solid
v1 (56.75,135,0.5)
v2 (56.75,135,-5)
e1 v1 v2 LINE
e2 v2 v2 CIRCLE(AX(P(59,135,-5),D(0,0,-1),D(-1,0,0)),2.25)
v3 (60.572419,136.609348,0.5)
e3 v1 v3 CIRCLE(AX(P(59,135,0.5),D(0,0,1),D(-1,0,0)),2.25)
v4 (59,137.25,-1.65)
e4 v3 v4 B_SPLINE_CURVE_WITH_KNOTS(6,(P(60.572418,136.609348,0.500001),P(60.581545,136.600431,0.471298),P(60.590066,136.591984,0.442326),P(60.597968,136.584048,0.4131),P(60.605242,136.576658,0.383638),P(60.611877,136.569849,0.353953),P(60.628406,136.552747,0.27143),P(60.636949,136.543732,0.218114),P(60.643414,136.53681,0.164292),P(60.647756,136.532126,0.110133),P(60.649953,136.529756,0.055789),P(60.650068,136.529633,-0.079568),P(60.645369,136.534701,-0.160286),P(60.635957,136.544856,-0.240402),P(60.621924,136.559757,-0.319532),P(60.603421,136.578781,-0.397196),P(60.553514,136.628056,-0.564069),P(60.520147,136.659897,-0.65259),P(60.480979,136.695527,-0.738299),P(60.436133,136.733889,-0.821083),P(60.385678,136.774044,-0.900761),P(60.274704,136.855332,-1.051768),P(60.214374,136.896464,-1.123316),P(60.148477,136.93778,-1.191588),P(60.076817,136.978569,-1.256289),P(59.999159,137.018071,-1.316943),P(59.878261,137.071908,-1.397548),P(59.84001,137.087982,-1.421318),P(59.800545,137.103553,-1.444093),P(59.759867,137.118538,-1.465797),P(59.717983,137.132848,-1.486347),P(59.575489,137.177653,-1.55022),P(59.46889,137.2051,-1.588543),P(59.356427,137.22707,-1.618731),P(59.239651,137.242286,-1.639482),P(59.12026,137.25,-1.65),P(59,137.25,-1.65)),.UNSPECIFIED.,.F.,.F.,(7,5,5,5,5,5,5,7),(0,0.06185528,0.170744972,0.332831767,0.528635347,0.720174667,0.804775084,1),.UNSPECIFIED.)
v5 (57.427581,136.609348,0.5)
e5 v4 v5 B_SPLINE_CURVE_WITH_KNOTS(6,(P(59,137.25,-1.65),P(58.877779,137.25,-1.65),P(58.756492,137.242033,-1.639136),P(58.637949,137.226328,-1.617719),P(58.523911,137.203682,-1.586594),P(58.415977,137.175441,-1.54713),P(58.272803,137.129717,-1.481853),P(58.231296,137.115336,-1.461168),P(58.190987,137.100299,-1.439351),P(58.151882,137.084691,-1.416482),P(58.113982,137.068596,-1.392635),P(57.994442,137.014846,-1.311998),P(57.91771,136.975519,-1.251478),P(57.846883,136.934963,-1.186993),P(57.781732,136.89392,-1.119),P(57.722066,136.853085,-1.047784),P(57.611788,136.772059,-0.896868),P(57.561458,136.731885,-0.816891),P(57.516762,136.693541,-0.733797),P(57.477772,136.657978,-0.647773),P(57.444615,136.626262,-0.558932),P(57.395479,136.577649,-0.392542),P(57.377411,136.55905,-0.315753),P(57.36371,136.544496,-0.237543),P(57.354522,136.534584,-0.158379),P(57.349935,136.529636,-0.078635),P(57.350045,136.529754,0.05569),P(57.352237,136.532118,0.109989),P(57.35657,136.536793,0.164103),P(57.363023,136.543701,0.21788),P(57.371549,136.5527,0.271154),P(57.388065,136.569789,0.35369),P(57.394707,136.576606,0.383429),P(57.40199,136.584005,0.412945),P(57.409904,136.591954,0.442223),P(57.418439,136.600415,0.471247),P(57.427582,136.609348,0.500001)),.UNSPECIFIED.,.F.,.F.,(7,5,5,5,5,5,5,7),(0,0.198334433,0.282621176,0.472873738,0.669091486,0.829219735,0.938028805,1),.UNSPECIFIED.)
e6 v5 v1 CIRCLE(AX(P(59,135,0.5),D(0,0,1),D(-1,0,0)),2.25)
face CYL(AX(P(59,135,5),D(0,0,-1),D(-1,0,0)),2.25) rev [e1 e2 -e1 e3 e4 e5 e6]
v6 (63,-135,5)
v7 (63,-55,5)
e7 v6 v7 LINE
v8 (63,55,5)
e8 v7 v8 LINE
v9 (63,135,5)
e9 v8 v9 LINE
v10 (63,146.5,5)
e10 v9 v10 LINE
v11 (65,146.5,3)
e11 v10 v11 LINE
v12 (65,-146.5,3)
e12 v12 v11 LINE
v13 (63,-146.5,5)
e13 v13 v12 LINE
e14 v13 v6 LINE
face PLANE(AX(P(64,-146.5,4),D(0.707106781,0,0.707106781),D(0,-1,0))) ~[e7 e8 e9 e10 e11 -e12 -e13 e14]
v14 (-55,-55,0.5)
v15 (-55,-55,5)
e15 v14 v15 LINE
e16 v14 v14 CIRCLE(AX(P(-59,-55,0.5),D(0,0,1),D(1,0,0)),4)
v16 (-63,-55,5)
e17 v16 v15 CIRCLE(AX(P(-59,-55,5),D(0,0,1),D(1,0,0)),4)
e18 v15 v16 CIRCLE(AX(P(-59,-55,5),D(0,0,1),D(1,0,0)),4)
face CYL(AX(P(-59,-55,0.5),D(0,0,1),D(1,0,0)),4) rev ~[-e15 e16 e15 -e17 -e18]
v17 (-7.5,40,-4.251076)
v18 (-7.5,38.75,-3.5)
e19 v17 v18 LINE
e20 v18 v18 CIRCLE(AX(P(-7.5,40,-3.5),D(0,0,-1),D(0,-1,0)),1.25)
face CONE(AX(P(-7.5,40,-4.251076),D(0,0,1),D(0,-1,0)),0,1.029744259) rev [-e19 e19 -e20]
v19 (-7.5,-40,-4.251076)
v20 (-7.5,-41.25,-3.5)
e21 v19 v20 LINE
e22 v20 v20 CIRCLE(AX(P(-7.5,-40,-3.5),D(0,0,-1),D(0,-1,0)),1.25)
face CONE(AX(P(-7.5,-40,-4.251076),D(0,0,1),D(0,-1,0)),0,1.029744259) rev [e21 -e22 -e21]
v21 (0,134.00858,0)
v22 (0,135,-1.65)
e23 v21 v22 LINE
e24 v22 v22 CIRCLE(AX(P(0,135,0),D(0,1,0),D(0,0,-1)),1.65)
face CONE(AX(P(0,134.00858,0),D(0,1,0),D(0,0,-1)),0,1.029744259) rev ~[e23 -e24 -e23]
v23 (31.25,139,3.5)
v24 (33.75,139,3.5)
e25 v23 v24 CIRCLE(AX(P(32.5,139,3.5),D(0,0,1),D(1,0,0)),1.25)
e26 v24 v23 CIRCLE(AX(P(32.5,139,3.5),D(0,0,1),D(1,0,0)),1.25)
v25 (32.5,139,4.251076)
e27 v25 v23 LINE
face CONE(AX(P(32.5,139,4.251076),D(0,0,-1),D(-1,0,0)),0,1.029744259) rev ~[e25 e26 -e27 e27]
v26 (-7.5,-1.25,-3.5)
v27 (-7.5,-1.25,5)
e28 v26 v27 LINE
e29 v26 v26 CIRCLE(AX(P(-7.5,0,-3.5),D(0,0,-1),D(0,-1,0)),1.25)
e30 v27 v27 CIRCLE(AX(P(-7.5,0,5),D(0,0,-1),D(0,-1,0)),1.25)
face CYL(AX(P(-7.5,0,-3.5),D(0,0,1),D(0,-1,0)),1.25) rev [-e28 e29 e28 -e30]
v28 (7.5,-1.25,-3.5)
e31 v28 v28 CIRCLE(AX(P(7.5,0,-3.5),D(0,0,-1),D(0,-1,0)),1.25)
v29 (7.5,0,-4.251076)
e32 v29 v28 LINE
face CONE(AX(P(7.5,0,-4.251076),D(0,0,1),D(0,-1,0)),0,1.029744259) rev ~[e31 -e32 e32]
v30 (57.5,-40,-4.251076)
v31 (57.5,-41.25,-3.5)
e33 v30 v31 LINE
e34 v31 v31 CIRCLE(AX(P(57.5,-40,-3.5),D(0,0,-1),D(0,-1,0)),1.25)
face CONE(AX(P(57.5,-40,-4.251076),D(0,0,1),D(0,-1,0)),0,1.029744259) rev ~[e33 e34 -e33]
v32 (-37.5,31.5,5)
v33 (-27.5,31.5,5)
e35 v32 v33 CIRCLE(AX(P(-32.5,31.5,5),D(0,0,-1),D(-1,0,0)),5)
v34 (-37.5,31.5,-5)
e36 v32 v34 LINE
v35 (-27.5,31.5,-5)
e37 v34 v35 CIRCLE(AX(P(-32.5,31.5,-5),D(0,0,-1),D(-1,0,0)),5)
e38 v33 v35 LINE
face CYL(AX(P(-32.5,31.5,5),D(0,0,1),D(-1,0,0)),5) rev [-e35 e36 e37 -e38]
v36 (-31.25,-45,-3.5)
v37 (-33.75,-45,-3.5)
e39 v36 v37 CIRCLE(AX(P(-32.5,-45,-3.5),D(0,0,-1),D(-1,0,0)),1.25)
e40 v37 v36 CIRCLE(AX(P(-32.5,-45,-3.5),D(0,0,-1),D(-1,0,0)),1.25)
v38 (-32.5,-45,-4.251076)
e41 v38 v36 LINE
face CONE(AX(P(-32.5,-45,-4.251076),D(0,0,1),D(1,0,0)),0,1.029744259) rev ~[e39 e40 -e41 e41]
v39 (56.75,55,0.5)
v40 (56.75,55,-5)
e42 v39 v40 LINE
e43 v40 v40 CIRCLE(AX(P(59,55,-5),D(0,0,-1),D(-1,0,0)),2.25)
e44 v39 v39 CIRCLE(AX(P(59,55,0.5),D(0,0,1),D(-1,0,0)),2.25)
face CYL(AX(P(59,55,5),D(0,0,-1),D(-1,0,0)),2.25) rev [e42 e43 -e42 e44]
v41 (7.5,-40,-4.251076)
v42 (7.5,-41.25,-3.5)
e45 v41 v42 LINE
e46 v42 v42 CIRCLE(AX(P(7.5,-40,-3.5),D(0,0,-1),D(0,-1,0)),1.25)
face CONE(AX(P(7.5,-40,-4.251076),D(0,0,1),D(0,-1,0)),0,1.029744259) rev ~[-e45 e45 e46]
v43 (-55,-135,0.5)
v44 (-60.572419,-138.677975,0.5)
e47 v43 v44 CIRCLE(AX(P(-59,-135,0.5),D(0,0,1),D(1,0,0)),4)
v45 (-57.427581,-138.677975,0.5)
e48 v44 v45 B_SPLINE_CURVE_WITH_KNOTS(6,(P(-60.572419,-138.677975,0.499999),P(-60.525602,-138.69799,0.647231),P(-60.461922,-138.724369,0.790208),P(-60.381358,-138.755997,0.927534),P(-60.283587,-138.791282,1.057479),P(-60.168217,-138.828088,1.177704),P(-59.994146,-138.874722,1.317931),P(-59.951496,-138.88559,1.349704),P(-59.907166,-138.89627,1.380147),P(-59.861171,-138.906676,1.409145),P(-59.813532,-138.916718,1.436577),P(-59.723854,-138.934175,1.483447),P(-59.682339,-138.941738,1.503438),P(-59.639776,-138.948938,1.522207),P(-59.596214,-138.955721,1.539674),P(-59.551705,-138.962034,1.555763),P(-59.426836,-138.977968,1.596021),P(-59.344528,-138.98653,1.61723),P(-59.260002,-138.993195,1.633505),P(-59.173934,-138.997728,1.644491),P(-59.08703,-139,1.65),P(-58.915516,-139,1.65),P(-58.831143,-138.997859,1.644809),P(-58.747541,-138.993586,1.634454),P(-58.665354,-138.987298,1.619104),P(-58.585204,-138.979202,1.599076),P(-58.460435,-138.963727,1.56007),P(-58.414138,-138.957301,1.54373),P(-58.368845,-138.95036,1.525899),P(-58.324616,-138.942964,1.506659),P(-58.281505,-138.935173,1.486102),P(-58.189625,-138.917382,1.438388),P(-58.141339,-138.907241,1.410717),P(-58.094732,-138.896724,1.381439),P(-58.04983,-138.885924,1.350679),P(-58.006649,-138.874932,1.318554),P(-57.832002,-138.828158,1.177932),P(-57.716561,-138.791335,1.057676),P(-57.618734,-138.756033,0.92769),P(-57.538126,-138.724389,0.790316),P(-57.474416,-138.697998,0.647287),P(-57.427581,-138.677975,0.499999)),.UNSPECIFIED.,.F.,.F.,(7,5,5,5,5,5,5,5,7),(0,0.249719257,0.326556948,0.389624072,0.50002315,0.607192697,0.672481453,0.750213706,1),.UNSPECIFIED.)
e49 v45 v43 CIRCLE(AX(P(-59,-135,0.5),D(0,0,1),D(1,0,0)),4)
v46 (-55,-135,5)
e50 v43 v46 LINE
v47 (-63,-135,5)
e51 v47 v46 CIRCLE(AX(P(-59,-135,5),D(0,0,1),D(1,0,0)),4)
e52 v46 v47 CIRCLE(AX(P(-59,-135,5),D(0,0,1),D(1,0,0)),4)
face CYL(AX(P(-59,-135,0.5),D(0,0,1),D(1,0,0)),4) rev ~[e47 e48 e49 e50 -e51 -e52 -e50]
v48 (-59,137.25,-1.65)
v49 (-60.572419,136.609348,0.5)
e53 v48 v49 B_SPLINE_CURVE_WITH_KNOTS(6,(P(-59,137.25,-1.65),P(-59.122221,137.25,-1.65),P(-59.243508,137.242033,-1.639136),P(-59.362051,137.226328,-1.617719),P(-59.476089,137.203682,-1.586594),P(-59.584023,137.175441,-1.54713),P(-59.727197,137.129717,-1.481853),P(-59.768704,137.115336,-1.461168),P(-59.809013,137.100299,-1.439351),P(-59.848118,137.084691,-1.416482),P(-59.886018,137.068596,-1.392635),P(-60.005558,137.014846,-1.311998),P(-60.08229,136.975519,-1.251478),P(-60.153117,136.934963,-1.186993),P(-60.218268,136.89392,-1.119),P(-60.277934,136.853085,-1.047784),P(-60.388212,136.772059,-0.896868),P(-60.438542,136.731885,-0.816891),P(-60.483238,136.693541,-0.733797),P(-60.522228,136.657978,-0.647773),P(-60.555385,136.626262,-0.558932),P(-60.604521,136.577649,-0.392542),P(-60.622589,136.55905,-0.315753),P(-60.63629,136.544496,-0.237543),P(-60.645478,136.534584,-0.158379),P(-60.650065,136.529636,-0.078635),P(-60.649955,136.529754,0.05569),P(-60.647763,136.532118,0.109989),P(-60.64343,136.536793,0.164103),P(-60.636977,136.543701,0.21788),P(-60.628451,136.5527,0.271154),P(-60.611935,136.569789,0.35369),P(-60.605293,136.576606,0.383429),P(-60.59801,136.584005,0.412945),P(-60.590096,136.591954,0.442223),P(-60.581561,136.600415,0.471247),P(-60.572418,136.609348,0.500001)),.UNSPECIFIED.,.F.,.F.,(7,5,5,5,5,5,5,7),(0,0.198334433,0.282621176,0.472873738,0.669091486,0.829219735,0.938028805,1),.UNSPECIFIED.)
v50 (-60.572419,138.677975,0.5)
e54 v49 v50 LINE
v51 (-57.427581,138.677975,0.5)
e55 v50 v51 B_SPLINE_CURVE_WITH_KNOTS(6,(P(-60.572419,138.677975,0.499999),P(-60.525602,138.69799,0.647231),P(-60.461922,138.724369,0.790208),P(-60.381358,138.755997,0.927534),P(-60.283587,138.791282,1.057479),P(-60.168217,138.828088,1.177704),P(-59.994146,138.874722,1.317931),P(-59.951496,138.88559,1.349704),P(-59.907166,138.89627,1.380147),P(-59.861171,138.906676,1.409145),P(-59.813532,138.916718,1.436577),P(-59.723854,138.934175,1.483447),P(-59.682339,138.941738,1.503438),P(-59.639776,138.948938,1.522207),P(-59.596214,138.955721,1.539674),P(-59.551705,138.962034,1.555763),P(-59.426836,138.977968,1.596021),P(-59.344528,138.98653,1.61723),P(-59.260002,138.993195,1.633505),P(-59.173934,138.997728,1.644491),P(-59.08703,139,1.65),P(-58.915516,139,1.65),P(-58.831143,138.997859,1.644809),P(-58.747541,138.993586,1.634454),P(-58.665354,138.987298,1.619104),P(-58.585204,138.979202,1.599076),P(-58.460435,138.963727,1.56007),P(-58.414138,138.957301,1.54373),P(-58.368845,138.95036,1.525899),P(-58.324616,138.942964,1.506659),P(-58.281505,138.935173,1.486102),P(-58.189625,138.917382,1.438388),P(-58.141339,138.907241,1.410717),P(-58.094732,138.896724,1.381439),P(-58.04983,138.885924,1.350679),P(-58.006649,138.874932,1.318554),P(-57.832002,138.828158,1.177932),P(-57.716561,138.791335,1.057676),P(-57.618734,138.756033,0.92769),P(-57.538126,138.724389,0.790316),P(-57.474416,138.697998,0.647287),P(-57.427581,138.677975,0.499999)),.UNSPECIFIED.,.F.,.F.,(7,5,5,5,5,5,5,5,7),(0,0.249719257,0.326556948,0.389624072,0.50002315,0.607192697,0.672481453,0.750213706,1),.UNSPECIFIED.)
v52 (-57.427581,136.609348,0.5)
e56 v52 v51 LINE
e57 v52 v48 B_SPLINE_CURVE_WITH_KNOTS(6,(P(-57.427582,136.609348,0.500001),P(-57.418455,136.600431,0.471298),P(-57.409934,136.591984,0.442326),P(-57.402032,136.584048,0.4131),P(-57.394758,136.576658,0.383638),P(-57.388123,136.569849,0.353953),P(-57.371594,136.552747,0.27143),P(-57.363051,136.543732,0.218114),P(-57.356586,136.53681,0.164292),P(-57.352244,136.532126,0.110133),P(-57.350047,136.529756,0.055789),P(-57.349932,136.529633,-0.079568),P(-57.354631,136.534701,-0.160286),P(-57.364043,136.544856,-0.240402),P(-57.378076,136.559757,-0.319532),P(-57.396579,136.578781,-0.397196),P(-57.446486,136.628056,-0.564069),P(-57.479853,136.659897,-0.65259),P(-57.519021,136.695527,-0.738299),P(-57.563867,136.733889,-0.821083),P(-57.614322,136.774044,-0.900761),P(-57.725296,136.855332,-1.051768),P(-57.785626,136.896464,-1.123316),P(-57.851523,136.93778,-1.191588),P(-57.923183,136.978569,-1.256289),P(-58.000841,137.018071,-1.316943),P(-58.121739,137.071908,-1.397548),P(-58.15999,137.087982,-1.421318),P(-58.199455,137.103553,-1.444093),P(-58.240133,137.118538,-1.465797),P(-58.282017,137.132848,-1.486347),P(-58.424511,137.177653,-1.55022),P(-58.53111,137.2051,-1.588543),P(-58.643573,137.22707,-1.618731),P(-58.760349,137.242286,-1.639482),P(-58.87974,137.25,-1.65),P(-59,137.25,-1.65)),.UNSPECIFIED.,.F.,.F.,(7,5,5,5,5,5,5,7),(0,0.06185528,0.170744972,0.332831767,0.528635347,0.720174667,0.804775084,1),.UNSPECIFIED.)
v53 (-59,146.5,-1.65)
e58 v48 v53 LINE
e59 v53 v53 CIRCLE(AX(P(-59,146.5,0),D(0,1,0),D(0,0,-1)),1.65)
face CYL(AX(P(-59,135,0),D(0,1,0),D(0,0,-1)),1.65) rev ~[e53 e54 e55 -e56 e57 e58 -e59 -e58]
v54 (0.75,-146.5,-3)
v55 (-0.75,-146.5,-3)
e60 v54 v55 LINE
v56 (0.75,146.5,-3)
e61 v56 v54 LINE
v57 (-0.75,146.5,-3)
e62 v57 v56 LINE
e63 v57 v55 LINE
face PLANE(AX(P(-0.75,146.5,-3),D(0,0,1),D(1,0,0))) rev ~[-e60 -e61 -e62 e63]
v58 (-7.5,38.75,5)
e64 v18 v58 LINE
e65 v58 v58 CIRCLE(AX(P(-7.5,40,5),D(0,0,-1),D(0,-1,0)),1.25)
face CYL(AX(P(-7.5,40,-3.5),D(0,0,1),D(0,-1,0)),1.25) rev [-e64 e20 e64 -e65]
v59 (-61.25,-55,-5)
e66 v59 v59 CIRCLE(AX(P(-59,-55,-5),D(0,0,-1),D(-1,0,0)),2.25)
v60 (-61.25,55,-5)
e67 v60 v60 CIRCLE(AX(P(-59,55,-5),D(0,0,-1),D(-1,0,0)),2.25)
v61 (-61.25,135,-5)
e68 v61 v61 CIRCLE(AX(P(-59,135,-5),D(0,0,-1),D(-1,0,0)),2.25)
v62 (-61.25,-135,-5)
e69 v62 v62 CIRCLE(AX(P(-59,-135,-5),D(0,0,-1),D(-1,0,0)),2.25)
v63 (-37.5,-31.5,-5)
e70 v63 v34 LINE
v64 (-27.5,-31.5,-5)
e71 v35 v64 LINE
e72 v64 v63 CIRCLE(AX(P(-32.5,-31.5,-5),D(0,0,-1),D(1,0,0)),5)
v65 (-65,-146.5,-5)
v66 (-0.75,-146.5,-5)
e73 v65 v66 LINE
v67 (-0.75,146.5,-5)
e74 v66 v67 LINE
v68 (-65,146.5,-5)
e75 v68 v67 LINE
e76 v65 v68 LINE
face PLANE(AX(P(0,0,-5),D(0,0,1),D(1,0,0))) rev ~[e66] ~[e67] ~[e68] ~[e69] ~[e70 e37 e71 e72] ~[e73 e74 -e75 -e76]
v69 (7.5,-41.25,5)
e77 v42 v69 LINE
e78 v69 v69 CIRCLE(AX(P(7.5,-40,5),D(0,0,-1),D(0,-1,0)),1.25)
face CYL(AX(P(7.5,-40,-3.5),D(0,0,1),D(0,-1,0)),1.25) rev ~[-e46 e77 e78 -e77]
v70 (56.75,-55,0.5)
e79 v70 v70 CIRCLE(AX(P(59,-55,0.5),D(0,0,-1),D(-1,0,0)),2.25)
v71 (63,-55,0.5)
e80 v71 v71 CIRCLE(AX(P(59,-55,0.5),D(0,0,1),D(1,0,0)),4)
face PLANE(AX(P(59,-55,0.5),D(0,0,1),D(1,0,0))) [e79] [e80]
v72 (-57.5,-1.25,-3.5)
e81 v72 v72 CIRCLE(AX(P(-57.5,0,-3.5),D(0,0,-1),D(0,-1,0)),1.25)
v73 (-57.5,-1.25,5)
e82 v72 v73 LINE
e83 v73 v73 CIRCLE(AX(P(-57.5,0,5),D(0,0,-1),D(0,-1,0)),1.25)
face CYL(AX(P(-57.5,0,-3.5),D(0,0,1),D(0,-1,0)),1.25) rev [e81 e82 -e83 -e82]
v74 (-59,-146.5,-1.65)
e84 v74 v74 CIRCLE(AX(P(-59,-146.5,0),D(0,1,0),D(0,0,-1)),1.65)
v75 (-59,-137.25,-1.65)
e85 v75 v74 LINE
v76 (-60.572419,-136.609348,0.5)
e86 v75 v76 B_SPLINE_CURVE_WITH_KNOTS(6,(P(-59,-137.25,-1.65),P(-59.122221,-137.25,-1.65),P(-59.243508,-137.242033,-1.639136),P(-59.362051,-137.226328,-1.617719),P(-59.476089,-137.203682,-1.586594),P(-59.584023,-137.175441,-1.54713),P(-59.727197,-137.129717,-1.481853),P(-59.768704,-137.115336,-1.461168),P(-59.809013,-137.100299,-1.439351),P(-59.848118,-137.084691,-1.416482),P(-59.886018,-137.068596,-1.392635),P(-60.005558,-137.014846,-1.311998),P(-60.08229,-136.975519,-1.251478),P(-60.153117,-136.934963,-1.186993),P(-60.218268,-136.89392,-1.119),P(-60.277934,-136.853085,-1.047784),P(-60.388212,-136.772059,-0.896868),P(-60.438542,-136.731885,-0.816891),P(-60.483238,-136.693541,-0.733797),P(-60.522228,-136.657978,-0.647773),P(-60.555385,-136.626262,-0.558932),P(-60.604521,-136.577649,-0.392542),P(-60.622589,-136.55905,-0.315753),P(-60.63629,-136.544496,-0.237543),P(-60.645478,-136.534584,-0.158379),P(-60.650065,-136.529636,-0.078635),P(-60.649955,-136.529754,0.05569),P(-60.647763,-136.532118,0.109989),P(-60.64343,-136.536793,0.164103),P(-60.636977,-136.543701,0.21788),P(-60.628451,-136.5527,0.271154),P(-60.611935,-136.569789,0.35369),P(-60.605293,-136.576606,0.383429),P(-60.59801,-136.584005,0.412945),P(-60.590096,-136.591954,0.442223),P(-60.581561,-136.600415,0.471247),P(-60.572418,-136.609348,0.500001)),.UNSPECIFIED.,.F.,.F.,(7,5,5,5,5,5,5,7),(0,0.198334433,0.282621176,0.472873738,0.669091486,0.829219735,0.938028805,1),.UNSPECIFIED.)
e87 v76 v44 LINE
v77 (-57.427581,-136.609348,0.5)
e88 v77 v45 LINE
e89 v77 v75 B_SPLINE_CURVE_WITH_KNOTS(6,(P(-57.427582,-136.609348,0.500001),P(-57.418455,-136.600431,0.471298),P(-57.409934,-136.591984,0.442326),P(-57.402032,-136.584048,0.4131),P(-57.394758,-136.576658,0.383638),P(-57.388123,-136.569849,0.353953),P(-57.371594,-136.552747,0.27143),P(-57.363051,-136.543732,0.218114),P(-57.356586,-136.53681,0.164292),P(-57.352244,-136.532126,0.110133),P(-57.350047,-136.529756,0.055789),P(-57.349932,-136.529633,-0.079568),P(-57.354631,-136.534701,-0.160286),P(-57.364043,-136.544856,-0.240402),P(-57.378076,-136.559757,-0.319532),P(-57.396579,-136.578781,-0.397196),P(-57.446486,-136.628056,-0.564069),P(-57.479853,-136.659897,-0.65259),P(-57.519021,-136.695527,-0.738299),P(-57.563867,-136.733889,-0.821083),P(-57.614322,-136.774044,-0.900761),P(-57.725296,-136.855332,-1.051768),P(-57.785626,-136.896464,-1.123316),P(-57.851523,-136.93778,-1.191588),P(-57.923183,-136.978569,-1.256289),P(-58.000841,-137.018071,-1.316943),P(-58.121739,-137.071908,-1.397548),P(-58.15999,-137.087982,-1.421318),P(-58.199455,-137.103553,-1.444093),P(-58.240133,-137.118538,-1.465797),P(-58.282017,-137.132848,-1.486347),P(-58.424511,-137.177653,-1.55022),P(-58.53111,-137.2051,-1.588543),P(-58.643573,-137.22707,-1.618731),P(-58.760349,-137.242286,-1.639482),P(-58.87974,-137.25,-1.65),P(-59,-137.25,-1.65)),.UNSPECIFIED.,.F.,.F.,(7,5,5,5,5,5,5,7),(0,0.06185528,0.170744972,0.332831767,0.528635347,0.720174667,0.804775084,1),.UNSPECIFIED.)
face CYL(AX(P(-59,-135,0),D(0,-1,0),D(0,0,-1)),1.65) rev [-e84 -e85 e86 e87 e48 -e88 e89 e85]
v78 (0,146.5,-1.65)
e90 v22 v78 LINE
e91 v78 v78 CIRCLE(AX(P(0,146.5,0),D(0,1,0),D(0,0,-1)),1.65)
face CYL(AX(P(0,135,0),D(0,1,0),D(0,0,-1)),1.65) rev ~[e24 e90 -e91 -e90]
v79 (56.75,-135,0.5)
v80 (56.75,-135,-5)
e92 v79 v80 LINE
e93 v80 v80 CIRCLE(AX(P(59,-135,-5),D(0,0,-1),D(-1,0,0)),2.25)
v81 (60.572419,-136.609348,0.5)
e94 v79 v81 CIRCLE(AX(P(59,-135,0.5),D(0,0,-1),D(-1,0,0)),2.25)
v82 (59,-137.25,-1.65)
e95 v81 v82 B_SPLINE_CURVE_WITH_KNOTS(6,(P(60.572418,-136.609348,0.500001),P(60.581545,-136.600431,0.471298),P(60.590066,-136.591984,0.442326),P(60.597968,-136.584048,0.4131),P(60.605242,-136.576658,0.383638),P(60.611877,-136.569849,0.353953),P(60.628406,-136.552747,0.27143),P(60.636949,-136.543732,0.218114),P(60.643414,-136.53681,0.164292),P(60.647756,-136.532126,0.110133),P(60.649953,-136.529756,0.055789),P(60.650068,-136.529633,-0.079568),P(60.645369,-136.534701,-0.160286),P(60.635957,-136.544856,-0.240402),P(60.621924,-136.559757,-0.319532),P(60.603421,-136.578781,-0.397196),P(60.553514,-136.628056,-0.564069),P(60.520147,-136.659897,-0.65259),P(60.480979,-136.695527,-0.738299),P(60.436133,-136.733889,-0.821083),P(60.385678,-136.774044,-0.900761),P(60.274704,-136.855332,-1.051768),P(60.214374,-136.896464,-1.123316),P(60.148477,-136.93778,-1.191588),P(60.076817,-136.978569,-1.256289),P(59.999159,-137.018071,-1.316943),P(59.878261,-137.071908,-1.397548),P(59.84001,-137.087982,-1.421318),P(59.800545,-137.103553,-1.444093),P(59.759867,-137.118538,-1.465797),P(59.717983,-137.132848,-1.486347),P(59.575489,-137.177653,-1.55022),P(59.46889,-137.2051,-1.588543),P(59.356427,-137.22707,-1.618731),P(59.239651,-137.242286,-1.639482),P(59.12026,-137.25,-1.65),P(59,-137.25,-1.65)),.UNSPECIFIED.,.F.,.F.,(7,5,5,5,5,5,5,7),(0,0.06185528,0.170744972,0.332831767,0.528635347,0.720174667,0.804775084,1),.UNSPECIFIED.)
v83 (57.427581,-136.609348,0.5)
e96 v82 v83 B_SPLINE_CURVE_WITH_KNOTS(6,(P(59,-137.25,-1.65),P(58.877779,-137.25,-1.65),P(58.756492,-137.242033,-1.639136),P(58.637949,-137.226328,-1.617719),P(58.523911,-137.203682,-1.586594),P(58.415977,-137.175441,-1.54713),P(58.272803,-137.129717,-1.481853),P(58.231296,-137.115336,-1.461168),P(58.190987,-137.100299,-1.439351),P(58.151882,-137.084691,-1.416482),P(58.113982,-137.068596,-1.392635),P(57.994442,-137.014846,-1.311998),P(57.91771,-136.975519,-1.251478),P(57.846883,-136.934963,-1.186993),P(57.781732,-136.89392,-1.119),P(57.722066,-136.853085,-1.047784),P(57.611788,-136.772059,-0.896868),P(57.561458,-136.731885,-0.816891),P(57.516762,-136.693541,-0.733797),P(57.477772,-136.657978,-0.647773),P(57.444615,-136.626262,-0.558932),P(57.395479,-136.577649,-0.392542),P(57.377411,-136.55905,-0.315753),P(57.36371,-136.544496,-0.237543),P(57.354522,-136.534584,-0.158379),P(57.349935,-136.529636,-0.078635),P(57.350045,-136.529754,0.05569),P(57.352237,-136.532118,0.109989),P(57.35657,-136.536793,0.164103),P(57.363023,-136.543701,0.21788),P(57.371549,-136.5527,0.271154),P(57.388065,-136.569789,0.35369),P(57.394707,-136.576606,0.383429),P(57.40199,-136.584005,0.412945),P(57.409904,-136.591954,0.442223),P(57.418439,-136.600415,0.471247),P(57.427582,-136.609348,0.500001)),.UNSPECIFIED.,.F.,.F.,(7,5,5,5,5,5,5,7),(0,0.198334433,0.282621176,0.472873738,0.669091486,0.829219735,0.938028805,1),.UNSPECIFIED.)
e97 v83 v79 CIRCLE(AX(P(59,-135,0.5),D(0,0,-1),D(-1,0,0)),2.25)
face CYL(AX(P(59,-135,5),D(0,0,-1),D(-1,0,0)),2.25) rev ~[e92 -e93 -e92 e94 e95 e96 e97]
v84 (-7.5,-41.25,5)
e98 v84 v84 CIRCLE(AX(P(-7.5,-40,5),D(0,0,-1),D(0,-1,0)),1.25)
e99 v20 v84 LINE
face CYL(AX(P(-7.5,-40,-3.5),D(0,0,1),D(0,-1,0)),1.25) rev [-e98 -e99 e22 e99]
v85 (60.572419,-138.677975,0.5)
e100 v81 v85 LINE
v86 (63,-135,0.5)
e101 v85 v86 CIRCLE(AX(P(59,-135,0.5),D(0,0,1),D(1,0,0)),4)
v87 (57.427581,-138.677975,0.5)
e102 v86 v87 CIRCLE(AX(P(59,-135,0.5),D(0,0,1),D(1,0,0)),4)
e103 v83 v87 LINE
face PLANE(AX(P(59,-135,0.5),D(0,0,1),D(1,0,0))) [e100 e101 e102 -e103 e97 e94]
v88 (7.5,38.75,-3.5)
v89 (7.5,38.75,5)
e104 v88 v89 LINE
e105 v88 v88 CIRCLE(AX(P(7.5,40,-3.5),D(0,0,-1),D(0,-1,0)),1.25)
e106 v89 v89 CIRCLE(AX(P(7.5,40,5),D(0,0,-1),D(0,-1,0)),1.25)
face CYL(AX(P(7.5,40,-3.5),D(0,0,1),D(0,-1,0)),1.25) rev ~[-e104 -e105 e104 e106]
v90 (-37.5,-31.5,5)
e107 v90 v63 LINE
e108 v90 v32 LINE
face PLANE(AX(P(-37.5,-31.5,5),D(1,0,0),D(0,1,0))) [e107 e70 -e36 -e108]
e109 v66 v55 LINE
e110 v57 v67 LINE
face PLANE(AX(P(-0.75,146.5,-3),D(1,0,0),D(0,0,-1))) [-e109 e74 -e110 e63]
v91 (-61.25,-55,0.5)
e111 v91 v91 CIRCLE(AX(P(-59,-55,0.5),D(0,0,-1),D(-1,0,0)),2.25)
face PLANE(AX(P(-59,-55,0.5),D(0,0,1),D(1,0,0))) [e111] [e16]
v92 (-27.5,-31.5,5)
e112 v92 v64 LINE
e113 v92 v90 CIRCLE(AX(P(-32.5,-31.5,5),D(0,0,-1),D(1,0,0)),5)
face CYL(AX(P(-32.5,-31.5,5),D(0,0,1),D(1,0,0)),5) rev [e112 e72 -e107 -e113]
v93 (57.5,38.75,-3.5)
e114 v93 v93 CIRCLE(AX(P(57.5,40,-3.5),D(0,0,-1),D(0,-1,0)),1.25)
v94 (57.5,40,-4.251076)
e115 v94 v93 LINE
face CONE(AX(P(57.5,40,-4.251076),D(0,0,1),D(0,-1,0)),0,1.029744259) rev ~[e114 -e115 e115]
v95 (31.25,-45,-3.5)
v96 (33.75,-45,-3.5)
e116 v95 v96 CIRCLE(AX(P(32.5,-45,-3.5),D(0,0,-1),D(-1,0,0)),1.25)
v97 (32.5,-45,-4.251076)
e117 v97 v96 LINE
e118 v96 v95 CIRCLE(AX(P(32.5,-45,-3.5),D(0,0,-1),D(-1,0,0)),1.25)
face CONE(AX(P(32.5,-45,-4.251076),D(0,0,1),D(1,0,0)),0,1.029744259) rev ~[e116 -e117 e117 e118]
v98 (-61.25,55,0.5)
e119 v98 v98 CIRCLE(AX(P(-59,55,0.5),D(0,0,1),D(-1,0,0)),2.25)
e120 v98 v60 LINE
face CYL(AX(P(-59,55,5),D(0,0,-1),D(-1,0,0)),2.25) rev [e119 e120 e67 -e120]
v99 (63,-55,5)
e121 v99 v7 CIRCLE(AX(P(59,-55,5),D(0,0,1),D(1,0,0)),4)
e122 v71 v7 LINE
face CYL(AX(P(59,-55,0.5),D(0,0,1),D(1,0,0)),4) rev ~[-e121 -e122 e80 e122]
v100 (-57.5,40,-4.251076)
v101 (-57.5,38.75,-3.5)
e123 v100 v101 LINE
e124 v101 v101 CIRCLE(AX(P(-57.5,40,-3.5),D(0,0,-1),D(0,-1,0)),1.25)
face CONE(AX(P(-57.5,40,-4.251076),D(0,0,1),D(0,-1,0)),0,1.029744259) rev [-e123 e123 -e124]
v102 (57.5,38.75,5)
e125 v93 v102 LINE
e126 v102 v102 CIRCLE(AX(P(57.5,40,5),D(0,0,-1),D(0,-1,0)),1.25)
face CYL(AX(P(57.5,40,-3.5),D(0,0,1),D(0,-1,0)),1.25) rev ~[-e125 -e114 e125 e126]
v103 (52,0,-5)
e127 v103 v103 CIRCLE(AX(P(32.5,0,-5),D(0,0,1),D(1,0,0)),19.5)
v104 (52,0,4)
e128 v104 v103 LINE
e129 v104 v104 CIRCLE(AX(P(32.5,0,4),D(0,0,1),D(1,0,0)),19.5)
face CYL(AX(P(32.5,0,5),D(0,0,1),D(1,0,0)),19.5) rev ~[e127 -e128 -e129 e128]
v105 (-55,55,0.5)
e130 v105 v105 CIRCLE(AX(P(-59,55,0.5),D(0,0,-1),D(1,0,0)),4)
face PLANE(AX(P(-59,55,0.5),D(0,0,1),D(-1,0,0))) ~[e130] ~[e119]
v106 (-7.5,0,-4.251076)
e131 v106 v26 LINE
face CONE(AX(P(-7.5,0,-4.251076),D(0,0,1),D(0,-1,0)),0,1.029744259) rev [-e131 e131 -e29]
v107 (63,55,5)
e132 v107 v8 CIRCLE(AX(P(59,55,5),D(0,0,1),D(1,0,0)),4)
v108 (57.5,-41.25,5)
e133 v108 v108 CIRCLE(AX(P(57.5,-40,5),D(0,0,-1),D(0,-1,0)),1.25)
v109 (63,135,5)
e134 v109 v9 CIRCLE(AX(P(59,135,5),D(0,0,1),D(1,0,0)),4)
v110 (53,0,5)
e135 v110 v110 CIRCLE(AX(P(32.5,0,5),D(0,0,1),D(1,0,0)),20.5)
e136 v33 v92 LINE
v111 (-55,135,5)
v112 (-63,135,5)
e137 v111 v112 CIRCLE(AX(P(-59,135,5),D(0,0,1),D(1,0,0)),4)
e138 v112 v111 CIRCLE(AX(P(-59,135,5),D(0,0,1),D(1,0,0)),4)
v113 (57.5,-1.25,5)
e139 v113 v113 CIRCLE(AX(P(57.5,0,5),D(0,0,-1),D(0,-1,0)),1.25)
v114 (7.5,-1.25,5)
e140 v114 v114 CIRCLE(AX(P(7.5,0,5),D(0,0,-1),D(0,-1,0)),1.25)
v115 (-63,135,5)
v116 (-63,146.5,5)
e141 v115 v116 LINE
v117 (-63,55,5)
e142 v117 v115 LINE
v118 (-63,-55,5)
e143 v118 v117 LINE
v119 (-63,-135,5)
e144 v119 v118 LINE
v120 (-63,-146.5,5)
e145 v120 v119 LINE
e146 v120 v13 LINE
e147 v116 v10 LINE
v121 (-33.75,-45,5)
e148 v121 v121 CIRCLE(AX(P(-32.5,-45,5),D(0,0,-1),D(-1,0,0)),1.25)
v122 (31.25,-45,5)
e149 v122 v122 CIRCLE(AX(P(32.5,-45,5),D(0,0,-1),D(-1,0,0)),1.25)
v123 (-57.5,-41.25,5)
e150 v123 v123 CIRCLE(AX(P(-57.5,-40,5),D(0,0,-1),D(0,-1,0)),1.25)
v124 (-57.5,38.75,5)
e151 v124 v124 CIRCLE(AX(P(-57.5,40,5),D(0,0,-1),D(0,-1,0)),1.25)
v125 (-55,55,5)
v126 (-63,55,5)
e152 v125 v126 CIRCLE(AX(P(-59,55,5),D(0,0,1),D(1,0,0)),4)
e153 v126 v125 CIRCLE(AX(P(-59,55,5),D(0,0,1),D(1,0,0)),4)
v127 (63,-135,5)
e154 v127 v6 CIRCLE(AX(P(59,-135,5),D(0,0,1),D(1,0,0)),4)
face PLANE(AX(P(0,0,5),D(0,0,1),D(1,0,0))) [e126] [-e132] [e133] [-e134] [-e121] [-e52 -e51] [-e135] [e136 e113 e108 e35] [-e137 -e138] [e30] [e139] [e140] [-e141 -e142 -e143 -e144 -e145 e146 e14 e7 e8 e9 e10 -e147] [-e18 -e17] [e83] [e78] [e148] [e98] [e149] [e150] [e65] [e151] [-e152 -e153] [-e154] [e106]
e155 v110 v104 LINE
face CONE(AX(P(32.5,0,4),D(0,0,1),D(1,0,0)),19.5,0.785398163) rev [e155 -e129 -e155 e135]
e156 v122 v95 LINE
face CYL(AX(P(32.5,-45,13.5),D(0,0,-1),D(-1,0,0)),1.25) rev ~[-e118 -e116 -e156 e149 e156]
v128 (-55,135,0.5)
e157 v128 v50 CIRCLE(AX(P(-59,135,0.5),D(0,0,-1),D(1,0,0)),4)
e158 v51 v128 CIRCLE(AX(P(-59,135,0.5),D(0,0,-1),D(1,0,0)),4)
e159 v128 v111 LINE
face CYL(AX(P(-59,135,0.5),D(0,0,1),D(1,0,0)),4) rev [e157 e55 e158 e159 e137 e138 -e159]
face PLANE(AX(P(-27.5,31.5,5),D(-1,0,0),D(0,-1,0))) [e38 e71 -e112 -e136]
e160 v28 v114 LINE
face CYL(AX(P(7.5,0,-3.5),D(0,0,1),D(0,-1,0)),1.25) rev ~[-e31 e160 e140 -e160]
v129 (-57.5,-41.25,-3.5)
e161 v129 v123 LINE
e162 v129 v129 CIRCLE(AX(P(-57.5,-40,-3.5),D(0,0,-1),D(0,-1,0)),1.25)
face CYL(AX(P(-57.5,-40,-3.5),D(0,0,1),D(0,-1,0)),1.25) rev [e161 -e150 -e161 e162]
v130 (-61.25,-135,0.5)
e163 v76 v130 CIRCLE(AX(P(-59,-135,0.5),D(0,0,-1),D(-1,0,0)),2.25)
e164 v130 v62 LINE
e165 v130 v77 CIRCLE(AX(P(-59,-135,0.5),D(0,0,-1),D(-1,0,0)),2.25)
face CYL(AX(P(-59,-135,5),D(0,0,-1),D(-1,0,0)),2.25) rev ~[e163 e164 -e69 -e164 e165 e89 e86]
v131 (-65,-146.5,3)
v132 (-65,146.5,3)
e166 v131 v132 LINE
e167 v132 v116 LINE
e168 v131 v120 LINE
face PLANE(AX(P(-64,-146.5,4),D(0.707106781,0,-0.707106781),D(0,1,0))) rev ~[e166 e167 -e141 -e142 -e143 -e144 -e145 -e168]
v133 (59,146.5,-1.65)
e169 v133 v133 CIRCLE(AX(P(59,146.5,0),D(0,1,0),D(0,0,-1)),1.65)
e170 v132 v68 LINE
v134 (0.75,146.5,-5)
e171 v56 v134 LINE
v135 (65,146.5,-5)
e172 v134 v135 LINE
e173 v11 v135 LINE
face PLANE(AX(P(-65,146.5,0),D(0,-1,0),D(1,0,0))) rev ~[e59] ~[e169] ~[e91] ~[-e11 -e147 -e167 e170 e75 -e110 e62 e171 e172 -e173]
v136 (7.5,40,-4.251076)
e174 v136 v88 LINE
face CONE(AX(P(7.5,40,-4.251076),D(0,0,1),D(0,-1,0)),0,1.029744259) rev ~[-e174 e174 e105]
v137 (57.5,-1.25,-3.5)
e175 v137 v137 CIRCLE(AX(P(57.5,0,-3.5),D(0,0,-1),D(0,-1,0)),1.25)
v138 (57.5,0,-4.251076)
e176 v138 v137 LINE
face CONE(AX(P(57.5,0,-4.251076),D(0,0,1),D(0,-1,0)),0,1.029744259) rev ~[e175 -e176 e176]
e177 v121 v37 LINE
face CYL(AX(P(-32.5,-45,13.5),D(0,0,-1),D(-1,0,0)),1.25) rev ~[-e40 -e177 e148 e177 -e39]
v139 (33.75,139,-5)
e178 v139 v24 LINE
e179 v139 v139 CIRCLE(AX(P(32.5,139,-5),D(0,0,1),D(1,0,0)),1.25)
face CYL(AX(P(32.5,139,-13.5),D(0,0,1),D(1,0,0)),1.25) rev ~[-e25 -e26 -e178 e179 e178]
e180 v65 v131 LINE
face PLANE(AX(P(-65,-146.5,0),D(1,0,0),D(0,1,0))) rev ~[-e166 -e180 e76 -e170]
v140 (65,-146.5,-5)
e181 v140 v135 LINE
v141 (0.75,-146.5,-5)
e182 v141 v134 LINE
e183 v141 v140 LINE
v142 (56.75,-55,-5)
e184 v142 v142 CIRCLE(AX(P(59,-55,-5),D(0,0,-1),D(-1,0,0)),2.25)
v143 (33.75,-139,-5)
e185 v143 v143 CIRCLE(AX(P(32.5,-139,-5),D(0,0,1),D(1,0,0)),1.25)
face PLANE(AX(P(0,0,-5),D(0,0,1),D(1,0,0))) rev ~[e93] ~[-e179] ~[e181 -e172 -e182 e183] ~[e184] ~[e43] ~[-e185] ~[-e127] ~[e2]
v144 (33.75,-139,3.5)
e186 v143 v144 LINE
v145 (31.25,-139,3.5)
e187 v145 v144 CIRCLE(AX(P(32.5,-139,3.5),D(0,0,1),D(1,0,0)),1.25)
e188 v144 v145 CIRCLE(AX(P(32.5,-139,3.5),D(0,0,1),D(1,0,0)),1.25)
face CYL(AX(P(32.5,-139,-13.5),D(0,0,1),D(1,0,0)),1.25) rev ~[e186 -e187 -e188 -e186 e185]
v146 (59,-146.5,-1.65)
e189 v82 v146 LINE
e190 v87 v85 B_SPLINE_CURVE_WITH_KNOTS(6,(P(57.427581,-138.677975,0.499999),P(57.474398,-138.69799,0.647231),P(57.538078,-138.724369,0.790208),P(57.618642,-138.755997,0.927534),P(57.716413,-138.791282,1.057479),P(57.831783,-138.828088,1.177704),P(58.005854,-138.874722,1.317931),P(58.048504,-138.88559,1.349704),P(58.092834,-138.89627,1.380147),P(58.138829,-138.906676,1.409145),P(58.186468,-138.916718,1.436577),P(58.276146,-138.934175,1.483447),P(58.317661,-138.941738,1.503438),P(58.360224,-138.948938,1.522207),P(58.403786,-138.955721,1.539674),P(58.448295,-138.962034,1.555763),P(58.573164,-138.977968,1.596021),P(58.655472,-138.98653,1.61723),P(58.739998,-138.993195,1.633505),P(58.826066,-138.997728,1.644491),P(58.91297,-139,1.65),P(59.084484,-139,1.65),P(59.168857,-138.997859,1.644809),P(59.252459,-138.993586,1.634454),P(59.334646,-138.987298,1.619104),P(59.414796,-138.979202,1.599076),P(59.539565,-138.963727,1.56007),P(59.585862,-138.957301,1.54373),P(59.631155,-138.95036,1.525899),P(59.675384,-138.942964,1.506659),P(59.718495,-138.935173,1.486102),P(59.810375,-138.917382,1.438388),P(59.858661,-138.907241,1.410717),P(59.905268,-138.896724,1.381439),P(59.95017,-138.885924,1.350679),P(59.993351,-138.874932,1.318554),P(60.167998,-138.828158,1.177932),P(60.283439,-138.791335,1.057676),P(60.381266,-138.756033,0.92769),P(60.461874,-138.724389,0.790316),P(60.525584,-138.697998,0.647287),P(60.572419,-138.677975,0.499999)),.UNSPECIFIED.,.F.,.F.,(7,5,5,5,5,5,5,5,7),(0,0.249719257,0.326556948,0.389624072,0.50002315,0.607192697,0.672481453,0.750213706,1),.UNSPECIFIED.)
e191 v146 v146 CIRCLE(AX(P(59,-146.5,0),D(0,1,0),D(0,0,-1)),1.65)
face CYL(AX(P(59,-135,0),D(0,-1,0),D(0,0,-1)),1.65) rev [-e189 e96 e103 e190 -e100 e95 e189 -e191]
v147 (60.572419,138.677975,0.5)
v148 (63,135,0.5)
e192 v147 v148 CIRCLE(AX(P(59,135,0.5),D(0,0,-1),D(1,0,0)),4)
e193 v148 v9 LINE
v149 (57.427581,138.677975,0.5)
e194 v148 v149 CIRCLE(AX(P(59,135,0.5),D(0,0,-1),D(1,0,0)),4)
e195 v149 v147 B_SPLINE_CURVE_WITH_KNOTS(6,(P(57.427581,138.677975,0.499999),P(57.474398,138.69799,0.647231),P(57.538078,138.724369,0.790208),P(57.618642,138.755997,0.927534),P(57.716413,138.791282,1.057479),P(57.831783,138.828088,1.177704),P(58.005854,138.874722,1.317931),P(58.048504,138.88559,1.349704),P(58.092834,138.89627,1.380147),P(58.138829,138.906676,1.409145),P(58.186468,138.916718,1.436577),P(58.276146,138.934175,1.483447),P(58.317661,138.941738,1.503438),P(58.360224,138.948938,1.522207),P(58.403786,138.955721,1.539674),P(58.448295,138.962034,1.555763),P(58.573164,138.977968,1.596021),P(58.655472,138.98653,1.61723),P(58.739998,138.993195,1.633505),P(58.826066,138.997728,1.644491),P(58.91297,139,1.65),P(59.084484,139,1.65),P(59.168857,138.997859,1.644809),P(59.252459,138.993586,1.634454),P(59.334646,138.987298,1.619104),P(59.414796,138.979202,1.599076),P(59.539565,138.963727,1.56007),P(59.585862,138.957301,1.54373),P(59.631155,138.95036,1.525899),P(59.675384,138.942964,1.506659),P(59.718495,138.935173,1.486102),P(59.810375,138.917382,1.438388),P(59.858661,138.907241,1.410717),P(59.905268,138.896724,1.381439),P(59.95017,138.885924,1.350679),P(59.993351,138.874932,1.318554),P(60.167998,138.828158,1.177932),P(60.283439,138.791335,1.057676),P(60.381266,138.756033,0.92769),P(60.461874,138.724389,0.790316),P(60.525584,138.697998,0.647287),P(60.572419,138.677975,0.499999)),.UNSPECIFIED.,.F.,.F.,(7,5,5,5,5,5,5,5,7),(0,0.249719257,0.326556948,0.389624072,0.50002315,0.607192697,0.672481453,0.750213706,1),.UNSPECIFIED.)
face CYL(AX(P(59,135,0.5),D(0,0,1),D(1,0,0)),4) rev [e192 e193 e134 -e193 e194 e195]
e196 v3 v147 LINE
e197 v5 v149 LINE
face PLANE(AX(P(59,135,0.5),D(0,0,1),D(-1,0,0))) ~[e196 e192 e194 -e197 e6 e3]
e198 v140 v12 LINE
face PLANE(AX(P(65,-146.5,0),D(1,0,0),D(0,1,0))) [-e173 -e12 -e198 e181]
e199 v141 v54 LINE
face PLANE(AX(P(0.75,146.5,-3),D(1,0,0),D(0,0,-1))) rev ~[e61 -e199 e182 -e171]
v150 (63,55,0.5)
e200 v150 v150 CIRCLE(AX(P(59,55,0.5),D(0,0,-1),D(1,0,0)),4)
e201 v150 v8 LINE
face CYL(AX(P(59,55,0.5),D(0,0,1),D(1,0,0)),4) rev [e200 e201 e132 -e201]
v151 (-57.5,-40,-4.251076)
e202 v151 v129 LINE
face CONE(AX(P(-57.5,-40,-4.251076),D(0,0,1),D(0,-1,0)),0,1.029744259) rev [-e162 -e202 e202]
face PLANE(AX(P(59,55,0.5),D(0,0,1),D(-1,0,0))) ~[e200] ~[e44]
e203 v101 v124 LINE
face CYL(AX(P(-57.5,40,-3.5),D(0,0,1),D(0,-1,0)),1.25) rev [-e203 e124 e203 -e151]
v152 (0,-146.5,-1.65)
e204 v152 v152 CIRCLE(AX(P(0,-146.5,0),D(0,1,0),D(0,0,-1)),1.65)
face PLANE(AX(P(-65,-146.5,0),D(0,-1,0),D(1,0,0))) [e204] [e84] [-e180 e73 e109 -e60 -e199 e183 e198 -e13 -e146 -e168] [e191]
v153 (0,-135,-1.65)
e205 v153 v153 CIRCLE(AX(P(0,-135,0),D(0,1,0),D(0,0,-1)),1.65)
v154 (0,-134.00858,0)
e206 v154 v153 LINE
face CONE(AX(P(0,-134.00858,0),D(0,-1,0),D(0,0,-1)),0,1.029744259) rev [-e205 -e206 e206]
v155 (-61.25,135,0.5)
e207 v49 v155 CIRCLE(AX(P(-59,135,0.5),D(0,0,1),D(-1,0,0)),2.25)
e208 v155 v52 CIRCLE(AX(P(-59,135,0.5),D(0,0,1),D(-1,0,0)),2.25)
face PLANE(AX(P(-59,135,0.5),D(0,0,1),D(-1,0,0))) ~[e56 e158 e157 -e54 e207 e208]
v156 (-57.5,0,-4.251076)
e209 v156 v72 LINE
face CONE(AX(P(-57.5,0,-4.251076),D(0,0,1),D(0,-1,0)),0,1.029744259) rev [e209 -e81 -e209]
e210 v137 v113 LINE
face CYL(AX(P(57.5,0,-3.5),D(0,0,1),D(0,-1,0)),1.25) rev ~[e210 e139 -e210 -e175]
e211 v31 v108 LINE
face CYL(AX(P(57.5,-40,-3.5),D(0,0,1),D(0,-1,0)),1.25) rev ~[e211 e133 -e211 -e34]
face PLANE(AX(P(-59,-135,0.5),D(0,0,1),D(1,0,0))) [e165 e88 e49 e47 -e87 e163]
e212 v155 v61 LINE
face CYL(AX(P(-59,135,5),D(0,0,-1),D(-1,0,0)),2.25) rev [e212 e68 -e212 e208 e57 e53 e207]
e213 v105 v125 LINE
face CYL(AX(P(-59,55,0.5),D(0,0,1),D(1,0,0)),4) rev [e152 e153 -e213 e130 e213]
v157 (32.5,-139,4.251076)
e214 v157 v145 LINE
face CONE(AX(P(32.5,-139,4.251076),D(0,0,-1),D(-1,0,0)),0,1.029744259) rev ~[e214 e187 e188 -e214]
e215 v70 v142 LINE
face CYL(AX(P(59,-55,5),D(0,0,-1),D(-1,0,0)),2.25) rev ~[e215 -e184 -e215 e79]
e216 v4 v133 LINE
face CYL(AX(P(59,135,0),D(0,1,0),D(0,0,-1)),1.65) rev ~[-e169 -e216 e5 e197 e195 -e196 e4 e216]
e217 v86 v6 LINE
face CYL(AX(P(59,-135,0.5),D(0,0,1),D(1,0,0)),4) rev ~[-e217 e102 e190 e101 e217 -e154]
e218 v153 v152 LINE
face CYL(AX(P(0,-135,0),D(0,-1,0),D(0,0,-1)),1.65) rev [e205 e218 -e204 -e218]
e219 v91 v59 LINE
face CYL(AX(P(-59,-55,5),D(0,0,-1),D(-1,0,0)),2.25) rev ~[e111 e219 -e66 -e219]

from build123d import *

# Parameters (mm, degrees)
SKETCH1_W                                            = 130
SKETCH1_H                                            = 293
BOSS_EXTRUDE1_DEPTH                                  = 5
SKETCH2_R                                            = 19.5
CUT_EXTRUDE1_DEPTH                                   = 161.584090121
CUT_EXTRUDE2_DEPTH                                   = 10
CHAMFER1_SIZE                                        = 2
HOLE_SIZE_PER_SOCKET_HEAD_CAP_SCREW_TYPE_D           = 4.5
HOLE_SIZE_PER_SOCKET_HEAD_CAP_SCREW_TYPE_CBORE_D     = 8
HOLE_SIZE_PER_SOCKET_HEAD_CAP_SCREW_TYPE_CBORE_DEPTH = 4.5
M3_TAPPED_HOLE1_AT_2_COUNT                           = 2
M3_TAPPED_HOLE1_AT_2_PITCH                           = 50
M3_TAPPED_HOLE1_AT_3_COUNT                           = 2
M3_TAPPED_HOLE1_AT_3_PITCH                           = 40
M3_TAPPED_HOLE1_AT_4_COUNT                           = 2
M3_TAPPED_HOLE1_AT_4_PITCH                           = 64.031242374
M3_TAPPED_HOLE1_AT_5_COUNT                           = 2
M3_TAPPED_HOLE1_AT_5_PITCH                           = 94.339811321
M3_TAPPED_HOLE1_AT_6_COUNT                           = 2
M3_TAPPED_HOLE1_AT_6_PITCH                           = 80
M3_TAPPED_HOLE2_D                                    = 2.5
M3_TAPPED_HOLE2_DEPTH                                = 8.5
M3_TAPPED_HOLE2_TIP                                  = 0.751075774
M4_TAPPED_HOLE1_AT_2_COUNT                           = 2
M4_TAPPED_HOLE1_AT_2_PITCH                           = 59
M4_TAPPED_HOLE1_AT_3_COUNT                           = 2
M4_TAPPED_HOLE1_AT_3_PITCH                           = 59
SKETCH12_W                                           = 1.5
SKETCH12_H                                           = 4
CUT_EXTRUDE3_DEPTH                                   = 301.164954749
M3_TAPPED_HOLE3_D                                    = 2.5
M3_TAPPED_HOLE3_DEPTH                                = 8.5
M3_TAPPED_HOLE3_TIP                                  = 0.751075774
CHAMFER2_SIZE                                        = 1


with BuildPart() as part:
    # Sketch1 → Boss-Extrude1 (new, symmetric)
    with BuildSketch(Plane.XY):
        Rectangle(SKETCH1_W, SKETCH1_H)
    extrude(amount=BOSS_EXTRUDE1_DEPTH, both=True)

    # Sketch2 → Cut-Extrude1 (cut, through all)
    with BuildSketch(Plane.XY.offset(5)):
        with Locations((32.5, 0)):
            Circle(SKETCH2_R)
    extrude(amount=-CUT_EXTRUDE1_DEPTH, mode=Mode.SUBTRACT)

    # Sketch3 → Cut-Extrude2 (cut)
    with BuildSketch(Plane.XY.offset(5)):
        with BuildLine():
            Line((-37.5, -31.5), (-37.5, 31.5))
            ThreePointArc((-37.5, 31.5), (-32.5, 36.5), (-27.5, 31.5))
            Line((-27.5, 31.5), (-27.5, -31.5))
            ThreePointArc((-27.5, -31.5), (-32.5, -36.5), (-37.5, -31.5))
        make_face()
    extrude(amount=-CUT_EXTRUDE2_DEPTH, mode=Mode.SUBTRACT)

    # Chamfer1
    chamfer1_edges = [part.edges().sort_by_distance(p)[0] for p in [
        (65, 0, 5),
        (-65, 0, 5),
    ]]
    chamfer(chamfer1_edges, length=CHAMFER1_SIZE)

    # Hole size per socket head cap screw type 1 (through all)
    with Locations(Plane.XY.offset(5)):
        with Locations((59, -135), (-59, -135), (59, -55), (-59, -55)):
            hole_size_per_socket_head_cap_screw_type = CounterBoreHole(HOLE_SIZE_PER_SOCKET_HEAD_CAP_SCREW_TYPE_D / 2, HOLE_SIZE_PER_SOCKET_HEAD_CAP_SCREW_TYPE_CBORE_D / 2, HOLE_SIZE_PER_SOCKET_HEAD_CAP_SCREW_TYPE_CBORE_DEPTH)

    # Mirror1: Hole size per socket head cap screw type 1 across plane
    add(hole_size_per_socket_head_cap_screw_type.mirror(Plane.ZX), mode=Mode.SUBTRACT)

    # Sketch6 → M3 Tapped Hole1 (revolve, cut)
    with BuildSketch(Plane(origin=(-7.5, -40, 5), x_dir=(0, -1, 0), z_dir=(1, 0, 0))):
        Polygon((0, 0), (0, 9.251075774), (1.25, 8.5), (1.25, 0), align=None)
    m3_tapped_hole1 = revolve(axis=Axis((-7.5, -40, 11.35), (0, 0, -1)), mode=Mode.SUBTRACT)

    # M3 Tapped Hole1 at 2: M3 Tapped Hole1 ×2
    with Locations(*[(-i * M3_TAPPED_HOLE1_AT_2_PITCH, 0, 0) for i in range(1, M3_TAPPED_HOLE1_AT_2_COUNT)]):
        add(m3_tapped_hole1, mode=Mode.SUBTRACT)

    # M3 Tapped Hole1 at 3: M3 Tapped Hole1 ×2
    with Locations(*[(0, i * M3_TAPPED_HOLE1_AT_3_PITCH, 0) for i in range(1, M3_TAPPED_HOLE1_AT_3_COUNT)]):
        add(m3_tapped_hole1, mode=Mode.SUBTRACT)

    # M3 Tapped Hole1 at 4: M3 Tapped Hole1 ×2
    with Locations(*[Vector(-0.7808688094430304, 0.6246950475544243, 0) * (i * M3_TAPPED_HOLE1_AT_4_PITCH) for i in range(1, M3_TAPPED_HOLE1_AT_4_COUNT)]):
        add(m3_tapped_hole1, mode=Mode.SUBTRACT)

    # M3 Tapped Hole1 at 5: M3 Tapped Hole1 ×2
    with Locations(*[Vector(-0.52999894000318, 0.847998304005088, 0) * (i * M3_TAPPED_HOLE1_AT_5_PITCH) for i in range(1, M3_TAPPED_HOLE1_AT_5_COUNT)]):
        add(m3_tapped_hole1, mode=Mode.SUBTRACT)

    # M3 Tapped Hole1 at 6: M3 Tapped Hole1 ×2
    with Locations(*[(0, i * M3_TAPPED_HOLE1_AT_6_PITCH, 0) for i in range(1, M3_TAPPED_HOLE1_AT_6_COUNT)]):
        add(m3_tapped_hole1, mode=Mode.SUBTRACT)

    # Mirror2: M3 Tapped Hole1 across plane
    add(m3_tapped_hole1.mirror(Plane.ZX), mode=Mode.SUBTRACT)

    # Mirror2 copy 1 sketch → Mirror2 copy 1 (revolve, cut)
    with BuildSketch(Plane(origin=(-57.5, 40, 5), x_dir=(0, 1, 0), z_dir=(1, 0, 0))):
        Polygon((0, 0), (0, -9.251075774), (1.25, -8.5), (1.25, 0), align=None)
    revolve(axis=Axis((-57.5, 40, 11.35), (0, 0, 1)), mode=Mode.SUBTRACT)

    # Mirror2 copy 2 sketch → Mirror2 copy 2 (revolve, cut)
    with BuildSketch(Plane(origin=(-7.5, 0, 5), x_dir=(0, 1, 0), z_dir=(1, 0, 0))):
        Polygon((0, 0), (0, -9.251075774), (1.25, -8.5), (1.25, 0), align=None)
    revolve(axis=Axis((-7.5, 0, 11.35), (0, 0, 1)), mode=Mode.SUBTRACT)

    # Mirror2 copy 3 sketch → Mirror2 copy 3 (revolve, cut)
    with BuildSketch(Plane(origin=(-57.5, 0, 5), x_dir=(0, 1, 0), z_dir=(1, 0, 0))):
        Polygon((0, 0), (0, -9.251075774), (1.25, -8.5), (1.25, 0), align=None)
    revolve(axis=Axis((-57.5, 0, 11.35), (0, 0, 1)), mode=Mode.SUBTRACT)

    # Mirror2 copy 4 sketch → Mirror2 copy 4 (revolve, cut)
    with BuildSketch(Plane(origin=(-57.5, -40, 5), x_dir=(0, 1, 0), z_dir=(1, 0, 0))):
        Polygon((0, 0), (0, -9.251075774), (1.25, -8.5), (1.25, 0), align=None)
    revolve(axis=Axis((-57.5, -40, 11.35), (0, 0, 1)), mode=Mode.SUBTRACT)

    # Mirror2 copy 5 sketch → Mirror2 copy 5 (revolve, cut)
    with BuildSketch(Plane(origin=(-7.5, -40, 5), x_dir=(0, 1, 0), z_dir=(1, 0, 0))):
        Polygon((0, 0), (0, -9.251075774), (1.25, -8.5), (1.25, 0), align=None)
    revolve(axis=Axis((-7.5, -40, 11.35), (0, 0, 1)), mode=Mode.SUBTRACT)

    # Mirror3: M3 Tapped Hole1 across plane
    add(m3_tapped_hole1.mirror(Plane(origin=(0, 0, 0), x_dir=(0, 0, 1), z_dir=(1, 0, 0))), mode=Mode.SUBTRACT)

    # Mirror3 copy 1 sketch → Mirror3 copy 1 (revolve, cut)
    with BuildSketch(Plane(origin=(57.5, -40, 5), x_dir=(0, -1, 0), z_dir=(-1, 0, 0))):
        Polygon((0, 0), (0, -9.251075774), (1.25, -8.5), (1.25, 0), align=None)
    revolve(axis=Axis((57.5, -40, 11.35), (0, 0, 1)), mode=Mode.SUBTRACT)

    # Mirror3 copy 2 sketch → Mirror3 copy 2 (revolve, cut)
    with BuildSketch(Plane(origin=(7.5, 0, 5), x_dir=(0, -1, 0), z_dir=(-1, 0, 0))):
        Polygon((0, 0), (0, -9.251075774), (1.25, -8.5), (1.25, 0), align=None)
    revolve(axis=Axis((7.5, 0, 11.35), (0, 0, 1)), mode=Mode.SUBTRACT)

    # Mirror3 copy 3 sketch → Mirror3 copy 3 (revolve, cut)
    with BuildSketch(Plane(origin=(57.5, 0, 5), x_dir=(0, -1, 0), z_dir=(-1, 0, 0))):
        Polygon((0, 0), (0, -9.251075774), (1.25, -8.5), (1.25, 0), align=None)
    revolve(axis=Axis((57.5, 0, 11.35), (0, 0, 1)), mode=Mode.SUBTRACT)

    # Mirror3 copy 4 sketch → Mirror3 copy 4 (revolve, cut)
    with BuildSketch(Plane(origin=(57.5, 40, 5), x_dir=(0, -1, 0), z_dir=(-1, 0, 0))):
        Polygon((0, 0), (0, -9.251075774), (1.25, -8.5), (1.25, 0), align=None)
    revolve(axis=Axis((57.5, 40, 11.35), (0, 0, 1)), mode=Mode.SUBTRACT)

    # Mirror3 copy 5 sketch → Mirror3 copy 5 (revolve, cut)
    with BuildSketch(Plane(origin=(7.5, 40, 5), x_dir=(0, -1, 0), z_dir=(-1, 0, 0))):
        Polygon((0, 0), (0, -9.251075774), (1.25, -8.5), (1.25, 0), align=None)
    revolve(axis=Axis((7.5, 40, 11.35), (0, 0, 1)), mode=Mode.SUBTRACT)

    # Mirror3 copy 6 sketch → Mirror3 copy 6 (revolve, cut)
    with BuildSketch(Plane(origin=(7.5, 40, 5), x_dir=(0, 1, 0), z_dir=(-1, 0, 0))):
        Polygon((0, 0), (0, 9.251075774), (1.25, 8.5), (1.25, 0), align=None)
    revolve(axis=Axis((7.5, 40, 11.35), (0, 0, -1)), mode=Mode.SUBTRACT)

    # Mirror3 copy 7 sketch → Mirror3 copy 7 (revolve, cut)
    with BuildSketch(Plane(origin=(57.5, 40, 5), x_dir=(0, 1, 0), z_dir=(-1, 0, 0))):
        Polygon((0, 0), (0, 9.251075774), (1.25, 8.5), (1.25, 0), align=None)
    revolve(axis=Axis((57.5, 40, 11.35), (0, 0, -1)), mode=Mode.SUBTRACT)

    # Mirror3 copy 8 sketch → Mirror3 copy 8 (revolve, cut)
    with BuildSketch(Plane(origin=(7.5, 0, 5), x_dir=(0, 1, 0), z_dir=(-1, 0, 0))):
        Polygon((0, 0), (0, 9.251075774), (1.25, 8.5), (1.25, 0), align=None)
    revolve(axis=Axis((7.5, 0, 11.35), (0, 0, -1)), mode=Mode.SUBTRACT)

    # Mirror3 copy 9 sketch → Mirror3 copy 9 (revolve, cut)
    with BuildSketch(Plane(origin=(57.5, 0, 5), x_dir=(0, 1, 0), z_dir=(-1, 0, 0))):
        Polygon((0, 0), (0, 9.251075774), (1.25, 8.5), (1.25, 0), align=None)
    revolve(axis=Axis((57.5, 0, 11.35), (0, 0, -1)), mode=Mode.SUBTRACT)

    # Mirror3 copy 10 sketch → Mirror3 copy 10 (revolve, cut)
    with BuildSketch(Plane(origin=(57.5, -40, 5), x_dir=(0, 1, 0), z_dir=(-1, 0, 0))):
        Polygon((0, 0), (0, 9.251075774), (1.25, 8.5), (1.25, 0), align=None)
    revolve(axis=Axis((57.5, -40, 11.35), (0, 0, -1)), mode=Mode.SUBTRACT)

    # Mirror3 copy 11 sketch → Mirror3 copy 11 (revolve, cut)
    with BuildSketch(Plane(origin=(7.5, -40, 5), x_dir=(0, 1, 0), z_dir=(-1, 0, 0))):
        Polygon((0, 0), (0, 9.251075774), (1.25, 8.5), (1.25, 0), align=None)
    revolve(axis=Axis((7.5, -40, 11.35), (0, 0, -1)), mode=Mode.SUBTRACT)

    # M3 Tapped Hole2
    with Locations(Plane(origin=(0, 0, -5), x_dir=(-1, 0, 0), z_dir=(0, 0, -1))):
        with Locations((-32.5, -139), (-32.5, 139)):
            Hole(M3_TAPPED_HOLE2_D / 2, depth=M3_TAPPED_HOLE2_DEPTH)
            with Locations((0, 0, -(M3_TAPPED_HOLE2_DEPTH + M3_TAPPED_HOLE2_TIP / 2))):  # 118° drill point
                Cone(0, M3_TAPPED_HOLE2_D / 2, M3_TAPPED_HOLE2_TIP, mode=Mode.SUBTRACT)

    # Sketch10 → M4 Tapped Hole1 (revolve, cut)
    with BuildSketch(Plane(origin=(0, -146.5, 0), x_dir=(0, 0, -1), z_dir=(1, 0, 0))):
        Polygon((0, 0), (0, 12.491420021), (1.65, 11.5), (1.65, 0), align=None)
    m4_tapped_hole1 = revolve(axis=Axis((0, -152.85, 0), (0, 1, 0)), mode=Mode.SUBTRACT)

    # M4 Tapped Hole1 at 2: M4 Tapped Hole1 ×2
    with Locations(*[(-i * M4_TAPPED_HOLE1_AT_2_PITCH, 0, 0) for i in range(1, M4_TAPPED_HOLE1_AT_2_COUNT)]):
        add(m4_tapped_hole1, mode=Mode.SUBTRACT)

    # M4 Tapped Hole1 at 3: M4 Tapped Hole1 ×2
    with Locations(*[(i * M4_TAPPED_HOLE1_AT_3_PITCH, 0, 0) for i in range(1, M4_TAPPED_HOLE1_AT_3_COUNT)]):
        add(m4_tapped_hole1, mode=Mode.SUBTRACT)

    # Mirror4: M4 Tapped Hole1 across plane
    add(m4_tapped_hole1.mirror(Plane.ZX), mode=Mode.SUBTRACT)

    # Mirror4 copy 1 sketch → Mirror4 copy 1 (revolve, cut)
    with BuildSketch(Plane(origin=(-59, 146.5, 0), x_dir=(0, 0, -1), z_dir=(1, 0, 0))):
        Polygon((0, 0), (0, -12.491420021), (1.65, -11.5), (1.65, 0), align=None)
    revolve(axis=Axis((-59, 152.85, 0), (0, 1, 0)), mode=Mode.SUBTRACT)

    # Mirror4 copy 2 sketch → Mirror4 copy 2 (revolve, cut)
    with BuildSketch(Plane(origin=(59, 146.5, 0), x_dir=(0, 0, -1), z_dir=(1, 0, 0))):
        Polygon((0, 0), (0, -12.491420021), (1.65, -11.5), (1.65, 0), align=None)
    revolve(axis=Axis((59, 152.85, 0), (0, 1, 0)), mode=Mode.SUBTRACT)

    # Sketch12 → Cut-Extrude3 (cut, through all)
    with BuildSketch(Plane(origin=(0, 146.5, 0), x_dir=(1, 0, 0), z_dir=(0, 1, 0))):
        with Locations((0, 5)):
            Rectangle(SKETCH12_W, SKETCH12_H)
    extrude(amount=-CUT_EXTRUDE3_DEPTH, mode=Mode.SUBTRACT)

    # M3 Tapped Hole3
    with Locations(Plane.XY.offset(5)):
        with Locations((-32.5, -45), (32.5, -45)):
            Hole(M3_TAPPED_HOLE3_D / 2, depth=M3_TAPPED_HOLE3_DEPTH)
            with Locations((0, 0, -(M3_TAPPED_HOLE3_DEPTH + M3_TAPPED_HOLE3_TIP / 2))):  # 118° drill point
                Cone(0, M3_TAPPED_HOLE3_D / 2, M3_TAPPED_HOLE3_TIP, mode=Mode.SUBTRACT)

    # Chamfer2
    chamfer2_edges = [part.edges().sort_by_distance(p)[0] for p in [
        (13, 0, 5),
    ]]
    chamfer(chamfer2_edges, length=CHAMFER2_SIZE)


solid = part.part
